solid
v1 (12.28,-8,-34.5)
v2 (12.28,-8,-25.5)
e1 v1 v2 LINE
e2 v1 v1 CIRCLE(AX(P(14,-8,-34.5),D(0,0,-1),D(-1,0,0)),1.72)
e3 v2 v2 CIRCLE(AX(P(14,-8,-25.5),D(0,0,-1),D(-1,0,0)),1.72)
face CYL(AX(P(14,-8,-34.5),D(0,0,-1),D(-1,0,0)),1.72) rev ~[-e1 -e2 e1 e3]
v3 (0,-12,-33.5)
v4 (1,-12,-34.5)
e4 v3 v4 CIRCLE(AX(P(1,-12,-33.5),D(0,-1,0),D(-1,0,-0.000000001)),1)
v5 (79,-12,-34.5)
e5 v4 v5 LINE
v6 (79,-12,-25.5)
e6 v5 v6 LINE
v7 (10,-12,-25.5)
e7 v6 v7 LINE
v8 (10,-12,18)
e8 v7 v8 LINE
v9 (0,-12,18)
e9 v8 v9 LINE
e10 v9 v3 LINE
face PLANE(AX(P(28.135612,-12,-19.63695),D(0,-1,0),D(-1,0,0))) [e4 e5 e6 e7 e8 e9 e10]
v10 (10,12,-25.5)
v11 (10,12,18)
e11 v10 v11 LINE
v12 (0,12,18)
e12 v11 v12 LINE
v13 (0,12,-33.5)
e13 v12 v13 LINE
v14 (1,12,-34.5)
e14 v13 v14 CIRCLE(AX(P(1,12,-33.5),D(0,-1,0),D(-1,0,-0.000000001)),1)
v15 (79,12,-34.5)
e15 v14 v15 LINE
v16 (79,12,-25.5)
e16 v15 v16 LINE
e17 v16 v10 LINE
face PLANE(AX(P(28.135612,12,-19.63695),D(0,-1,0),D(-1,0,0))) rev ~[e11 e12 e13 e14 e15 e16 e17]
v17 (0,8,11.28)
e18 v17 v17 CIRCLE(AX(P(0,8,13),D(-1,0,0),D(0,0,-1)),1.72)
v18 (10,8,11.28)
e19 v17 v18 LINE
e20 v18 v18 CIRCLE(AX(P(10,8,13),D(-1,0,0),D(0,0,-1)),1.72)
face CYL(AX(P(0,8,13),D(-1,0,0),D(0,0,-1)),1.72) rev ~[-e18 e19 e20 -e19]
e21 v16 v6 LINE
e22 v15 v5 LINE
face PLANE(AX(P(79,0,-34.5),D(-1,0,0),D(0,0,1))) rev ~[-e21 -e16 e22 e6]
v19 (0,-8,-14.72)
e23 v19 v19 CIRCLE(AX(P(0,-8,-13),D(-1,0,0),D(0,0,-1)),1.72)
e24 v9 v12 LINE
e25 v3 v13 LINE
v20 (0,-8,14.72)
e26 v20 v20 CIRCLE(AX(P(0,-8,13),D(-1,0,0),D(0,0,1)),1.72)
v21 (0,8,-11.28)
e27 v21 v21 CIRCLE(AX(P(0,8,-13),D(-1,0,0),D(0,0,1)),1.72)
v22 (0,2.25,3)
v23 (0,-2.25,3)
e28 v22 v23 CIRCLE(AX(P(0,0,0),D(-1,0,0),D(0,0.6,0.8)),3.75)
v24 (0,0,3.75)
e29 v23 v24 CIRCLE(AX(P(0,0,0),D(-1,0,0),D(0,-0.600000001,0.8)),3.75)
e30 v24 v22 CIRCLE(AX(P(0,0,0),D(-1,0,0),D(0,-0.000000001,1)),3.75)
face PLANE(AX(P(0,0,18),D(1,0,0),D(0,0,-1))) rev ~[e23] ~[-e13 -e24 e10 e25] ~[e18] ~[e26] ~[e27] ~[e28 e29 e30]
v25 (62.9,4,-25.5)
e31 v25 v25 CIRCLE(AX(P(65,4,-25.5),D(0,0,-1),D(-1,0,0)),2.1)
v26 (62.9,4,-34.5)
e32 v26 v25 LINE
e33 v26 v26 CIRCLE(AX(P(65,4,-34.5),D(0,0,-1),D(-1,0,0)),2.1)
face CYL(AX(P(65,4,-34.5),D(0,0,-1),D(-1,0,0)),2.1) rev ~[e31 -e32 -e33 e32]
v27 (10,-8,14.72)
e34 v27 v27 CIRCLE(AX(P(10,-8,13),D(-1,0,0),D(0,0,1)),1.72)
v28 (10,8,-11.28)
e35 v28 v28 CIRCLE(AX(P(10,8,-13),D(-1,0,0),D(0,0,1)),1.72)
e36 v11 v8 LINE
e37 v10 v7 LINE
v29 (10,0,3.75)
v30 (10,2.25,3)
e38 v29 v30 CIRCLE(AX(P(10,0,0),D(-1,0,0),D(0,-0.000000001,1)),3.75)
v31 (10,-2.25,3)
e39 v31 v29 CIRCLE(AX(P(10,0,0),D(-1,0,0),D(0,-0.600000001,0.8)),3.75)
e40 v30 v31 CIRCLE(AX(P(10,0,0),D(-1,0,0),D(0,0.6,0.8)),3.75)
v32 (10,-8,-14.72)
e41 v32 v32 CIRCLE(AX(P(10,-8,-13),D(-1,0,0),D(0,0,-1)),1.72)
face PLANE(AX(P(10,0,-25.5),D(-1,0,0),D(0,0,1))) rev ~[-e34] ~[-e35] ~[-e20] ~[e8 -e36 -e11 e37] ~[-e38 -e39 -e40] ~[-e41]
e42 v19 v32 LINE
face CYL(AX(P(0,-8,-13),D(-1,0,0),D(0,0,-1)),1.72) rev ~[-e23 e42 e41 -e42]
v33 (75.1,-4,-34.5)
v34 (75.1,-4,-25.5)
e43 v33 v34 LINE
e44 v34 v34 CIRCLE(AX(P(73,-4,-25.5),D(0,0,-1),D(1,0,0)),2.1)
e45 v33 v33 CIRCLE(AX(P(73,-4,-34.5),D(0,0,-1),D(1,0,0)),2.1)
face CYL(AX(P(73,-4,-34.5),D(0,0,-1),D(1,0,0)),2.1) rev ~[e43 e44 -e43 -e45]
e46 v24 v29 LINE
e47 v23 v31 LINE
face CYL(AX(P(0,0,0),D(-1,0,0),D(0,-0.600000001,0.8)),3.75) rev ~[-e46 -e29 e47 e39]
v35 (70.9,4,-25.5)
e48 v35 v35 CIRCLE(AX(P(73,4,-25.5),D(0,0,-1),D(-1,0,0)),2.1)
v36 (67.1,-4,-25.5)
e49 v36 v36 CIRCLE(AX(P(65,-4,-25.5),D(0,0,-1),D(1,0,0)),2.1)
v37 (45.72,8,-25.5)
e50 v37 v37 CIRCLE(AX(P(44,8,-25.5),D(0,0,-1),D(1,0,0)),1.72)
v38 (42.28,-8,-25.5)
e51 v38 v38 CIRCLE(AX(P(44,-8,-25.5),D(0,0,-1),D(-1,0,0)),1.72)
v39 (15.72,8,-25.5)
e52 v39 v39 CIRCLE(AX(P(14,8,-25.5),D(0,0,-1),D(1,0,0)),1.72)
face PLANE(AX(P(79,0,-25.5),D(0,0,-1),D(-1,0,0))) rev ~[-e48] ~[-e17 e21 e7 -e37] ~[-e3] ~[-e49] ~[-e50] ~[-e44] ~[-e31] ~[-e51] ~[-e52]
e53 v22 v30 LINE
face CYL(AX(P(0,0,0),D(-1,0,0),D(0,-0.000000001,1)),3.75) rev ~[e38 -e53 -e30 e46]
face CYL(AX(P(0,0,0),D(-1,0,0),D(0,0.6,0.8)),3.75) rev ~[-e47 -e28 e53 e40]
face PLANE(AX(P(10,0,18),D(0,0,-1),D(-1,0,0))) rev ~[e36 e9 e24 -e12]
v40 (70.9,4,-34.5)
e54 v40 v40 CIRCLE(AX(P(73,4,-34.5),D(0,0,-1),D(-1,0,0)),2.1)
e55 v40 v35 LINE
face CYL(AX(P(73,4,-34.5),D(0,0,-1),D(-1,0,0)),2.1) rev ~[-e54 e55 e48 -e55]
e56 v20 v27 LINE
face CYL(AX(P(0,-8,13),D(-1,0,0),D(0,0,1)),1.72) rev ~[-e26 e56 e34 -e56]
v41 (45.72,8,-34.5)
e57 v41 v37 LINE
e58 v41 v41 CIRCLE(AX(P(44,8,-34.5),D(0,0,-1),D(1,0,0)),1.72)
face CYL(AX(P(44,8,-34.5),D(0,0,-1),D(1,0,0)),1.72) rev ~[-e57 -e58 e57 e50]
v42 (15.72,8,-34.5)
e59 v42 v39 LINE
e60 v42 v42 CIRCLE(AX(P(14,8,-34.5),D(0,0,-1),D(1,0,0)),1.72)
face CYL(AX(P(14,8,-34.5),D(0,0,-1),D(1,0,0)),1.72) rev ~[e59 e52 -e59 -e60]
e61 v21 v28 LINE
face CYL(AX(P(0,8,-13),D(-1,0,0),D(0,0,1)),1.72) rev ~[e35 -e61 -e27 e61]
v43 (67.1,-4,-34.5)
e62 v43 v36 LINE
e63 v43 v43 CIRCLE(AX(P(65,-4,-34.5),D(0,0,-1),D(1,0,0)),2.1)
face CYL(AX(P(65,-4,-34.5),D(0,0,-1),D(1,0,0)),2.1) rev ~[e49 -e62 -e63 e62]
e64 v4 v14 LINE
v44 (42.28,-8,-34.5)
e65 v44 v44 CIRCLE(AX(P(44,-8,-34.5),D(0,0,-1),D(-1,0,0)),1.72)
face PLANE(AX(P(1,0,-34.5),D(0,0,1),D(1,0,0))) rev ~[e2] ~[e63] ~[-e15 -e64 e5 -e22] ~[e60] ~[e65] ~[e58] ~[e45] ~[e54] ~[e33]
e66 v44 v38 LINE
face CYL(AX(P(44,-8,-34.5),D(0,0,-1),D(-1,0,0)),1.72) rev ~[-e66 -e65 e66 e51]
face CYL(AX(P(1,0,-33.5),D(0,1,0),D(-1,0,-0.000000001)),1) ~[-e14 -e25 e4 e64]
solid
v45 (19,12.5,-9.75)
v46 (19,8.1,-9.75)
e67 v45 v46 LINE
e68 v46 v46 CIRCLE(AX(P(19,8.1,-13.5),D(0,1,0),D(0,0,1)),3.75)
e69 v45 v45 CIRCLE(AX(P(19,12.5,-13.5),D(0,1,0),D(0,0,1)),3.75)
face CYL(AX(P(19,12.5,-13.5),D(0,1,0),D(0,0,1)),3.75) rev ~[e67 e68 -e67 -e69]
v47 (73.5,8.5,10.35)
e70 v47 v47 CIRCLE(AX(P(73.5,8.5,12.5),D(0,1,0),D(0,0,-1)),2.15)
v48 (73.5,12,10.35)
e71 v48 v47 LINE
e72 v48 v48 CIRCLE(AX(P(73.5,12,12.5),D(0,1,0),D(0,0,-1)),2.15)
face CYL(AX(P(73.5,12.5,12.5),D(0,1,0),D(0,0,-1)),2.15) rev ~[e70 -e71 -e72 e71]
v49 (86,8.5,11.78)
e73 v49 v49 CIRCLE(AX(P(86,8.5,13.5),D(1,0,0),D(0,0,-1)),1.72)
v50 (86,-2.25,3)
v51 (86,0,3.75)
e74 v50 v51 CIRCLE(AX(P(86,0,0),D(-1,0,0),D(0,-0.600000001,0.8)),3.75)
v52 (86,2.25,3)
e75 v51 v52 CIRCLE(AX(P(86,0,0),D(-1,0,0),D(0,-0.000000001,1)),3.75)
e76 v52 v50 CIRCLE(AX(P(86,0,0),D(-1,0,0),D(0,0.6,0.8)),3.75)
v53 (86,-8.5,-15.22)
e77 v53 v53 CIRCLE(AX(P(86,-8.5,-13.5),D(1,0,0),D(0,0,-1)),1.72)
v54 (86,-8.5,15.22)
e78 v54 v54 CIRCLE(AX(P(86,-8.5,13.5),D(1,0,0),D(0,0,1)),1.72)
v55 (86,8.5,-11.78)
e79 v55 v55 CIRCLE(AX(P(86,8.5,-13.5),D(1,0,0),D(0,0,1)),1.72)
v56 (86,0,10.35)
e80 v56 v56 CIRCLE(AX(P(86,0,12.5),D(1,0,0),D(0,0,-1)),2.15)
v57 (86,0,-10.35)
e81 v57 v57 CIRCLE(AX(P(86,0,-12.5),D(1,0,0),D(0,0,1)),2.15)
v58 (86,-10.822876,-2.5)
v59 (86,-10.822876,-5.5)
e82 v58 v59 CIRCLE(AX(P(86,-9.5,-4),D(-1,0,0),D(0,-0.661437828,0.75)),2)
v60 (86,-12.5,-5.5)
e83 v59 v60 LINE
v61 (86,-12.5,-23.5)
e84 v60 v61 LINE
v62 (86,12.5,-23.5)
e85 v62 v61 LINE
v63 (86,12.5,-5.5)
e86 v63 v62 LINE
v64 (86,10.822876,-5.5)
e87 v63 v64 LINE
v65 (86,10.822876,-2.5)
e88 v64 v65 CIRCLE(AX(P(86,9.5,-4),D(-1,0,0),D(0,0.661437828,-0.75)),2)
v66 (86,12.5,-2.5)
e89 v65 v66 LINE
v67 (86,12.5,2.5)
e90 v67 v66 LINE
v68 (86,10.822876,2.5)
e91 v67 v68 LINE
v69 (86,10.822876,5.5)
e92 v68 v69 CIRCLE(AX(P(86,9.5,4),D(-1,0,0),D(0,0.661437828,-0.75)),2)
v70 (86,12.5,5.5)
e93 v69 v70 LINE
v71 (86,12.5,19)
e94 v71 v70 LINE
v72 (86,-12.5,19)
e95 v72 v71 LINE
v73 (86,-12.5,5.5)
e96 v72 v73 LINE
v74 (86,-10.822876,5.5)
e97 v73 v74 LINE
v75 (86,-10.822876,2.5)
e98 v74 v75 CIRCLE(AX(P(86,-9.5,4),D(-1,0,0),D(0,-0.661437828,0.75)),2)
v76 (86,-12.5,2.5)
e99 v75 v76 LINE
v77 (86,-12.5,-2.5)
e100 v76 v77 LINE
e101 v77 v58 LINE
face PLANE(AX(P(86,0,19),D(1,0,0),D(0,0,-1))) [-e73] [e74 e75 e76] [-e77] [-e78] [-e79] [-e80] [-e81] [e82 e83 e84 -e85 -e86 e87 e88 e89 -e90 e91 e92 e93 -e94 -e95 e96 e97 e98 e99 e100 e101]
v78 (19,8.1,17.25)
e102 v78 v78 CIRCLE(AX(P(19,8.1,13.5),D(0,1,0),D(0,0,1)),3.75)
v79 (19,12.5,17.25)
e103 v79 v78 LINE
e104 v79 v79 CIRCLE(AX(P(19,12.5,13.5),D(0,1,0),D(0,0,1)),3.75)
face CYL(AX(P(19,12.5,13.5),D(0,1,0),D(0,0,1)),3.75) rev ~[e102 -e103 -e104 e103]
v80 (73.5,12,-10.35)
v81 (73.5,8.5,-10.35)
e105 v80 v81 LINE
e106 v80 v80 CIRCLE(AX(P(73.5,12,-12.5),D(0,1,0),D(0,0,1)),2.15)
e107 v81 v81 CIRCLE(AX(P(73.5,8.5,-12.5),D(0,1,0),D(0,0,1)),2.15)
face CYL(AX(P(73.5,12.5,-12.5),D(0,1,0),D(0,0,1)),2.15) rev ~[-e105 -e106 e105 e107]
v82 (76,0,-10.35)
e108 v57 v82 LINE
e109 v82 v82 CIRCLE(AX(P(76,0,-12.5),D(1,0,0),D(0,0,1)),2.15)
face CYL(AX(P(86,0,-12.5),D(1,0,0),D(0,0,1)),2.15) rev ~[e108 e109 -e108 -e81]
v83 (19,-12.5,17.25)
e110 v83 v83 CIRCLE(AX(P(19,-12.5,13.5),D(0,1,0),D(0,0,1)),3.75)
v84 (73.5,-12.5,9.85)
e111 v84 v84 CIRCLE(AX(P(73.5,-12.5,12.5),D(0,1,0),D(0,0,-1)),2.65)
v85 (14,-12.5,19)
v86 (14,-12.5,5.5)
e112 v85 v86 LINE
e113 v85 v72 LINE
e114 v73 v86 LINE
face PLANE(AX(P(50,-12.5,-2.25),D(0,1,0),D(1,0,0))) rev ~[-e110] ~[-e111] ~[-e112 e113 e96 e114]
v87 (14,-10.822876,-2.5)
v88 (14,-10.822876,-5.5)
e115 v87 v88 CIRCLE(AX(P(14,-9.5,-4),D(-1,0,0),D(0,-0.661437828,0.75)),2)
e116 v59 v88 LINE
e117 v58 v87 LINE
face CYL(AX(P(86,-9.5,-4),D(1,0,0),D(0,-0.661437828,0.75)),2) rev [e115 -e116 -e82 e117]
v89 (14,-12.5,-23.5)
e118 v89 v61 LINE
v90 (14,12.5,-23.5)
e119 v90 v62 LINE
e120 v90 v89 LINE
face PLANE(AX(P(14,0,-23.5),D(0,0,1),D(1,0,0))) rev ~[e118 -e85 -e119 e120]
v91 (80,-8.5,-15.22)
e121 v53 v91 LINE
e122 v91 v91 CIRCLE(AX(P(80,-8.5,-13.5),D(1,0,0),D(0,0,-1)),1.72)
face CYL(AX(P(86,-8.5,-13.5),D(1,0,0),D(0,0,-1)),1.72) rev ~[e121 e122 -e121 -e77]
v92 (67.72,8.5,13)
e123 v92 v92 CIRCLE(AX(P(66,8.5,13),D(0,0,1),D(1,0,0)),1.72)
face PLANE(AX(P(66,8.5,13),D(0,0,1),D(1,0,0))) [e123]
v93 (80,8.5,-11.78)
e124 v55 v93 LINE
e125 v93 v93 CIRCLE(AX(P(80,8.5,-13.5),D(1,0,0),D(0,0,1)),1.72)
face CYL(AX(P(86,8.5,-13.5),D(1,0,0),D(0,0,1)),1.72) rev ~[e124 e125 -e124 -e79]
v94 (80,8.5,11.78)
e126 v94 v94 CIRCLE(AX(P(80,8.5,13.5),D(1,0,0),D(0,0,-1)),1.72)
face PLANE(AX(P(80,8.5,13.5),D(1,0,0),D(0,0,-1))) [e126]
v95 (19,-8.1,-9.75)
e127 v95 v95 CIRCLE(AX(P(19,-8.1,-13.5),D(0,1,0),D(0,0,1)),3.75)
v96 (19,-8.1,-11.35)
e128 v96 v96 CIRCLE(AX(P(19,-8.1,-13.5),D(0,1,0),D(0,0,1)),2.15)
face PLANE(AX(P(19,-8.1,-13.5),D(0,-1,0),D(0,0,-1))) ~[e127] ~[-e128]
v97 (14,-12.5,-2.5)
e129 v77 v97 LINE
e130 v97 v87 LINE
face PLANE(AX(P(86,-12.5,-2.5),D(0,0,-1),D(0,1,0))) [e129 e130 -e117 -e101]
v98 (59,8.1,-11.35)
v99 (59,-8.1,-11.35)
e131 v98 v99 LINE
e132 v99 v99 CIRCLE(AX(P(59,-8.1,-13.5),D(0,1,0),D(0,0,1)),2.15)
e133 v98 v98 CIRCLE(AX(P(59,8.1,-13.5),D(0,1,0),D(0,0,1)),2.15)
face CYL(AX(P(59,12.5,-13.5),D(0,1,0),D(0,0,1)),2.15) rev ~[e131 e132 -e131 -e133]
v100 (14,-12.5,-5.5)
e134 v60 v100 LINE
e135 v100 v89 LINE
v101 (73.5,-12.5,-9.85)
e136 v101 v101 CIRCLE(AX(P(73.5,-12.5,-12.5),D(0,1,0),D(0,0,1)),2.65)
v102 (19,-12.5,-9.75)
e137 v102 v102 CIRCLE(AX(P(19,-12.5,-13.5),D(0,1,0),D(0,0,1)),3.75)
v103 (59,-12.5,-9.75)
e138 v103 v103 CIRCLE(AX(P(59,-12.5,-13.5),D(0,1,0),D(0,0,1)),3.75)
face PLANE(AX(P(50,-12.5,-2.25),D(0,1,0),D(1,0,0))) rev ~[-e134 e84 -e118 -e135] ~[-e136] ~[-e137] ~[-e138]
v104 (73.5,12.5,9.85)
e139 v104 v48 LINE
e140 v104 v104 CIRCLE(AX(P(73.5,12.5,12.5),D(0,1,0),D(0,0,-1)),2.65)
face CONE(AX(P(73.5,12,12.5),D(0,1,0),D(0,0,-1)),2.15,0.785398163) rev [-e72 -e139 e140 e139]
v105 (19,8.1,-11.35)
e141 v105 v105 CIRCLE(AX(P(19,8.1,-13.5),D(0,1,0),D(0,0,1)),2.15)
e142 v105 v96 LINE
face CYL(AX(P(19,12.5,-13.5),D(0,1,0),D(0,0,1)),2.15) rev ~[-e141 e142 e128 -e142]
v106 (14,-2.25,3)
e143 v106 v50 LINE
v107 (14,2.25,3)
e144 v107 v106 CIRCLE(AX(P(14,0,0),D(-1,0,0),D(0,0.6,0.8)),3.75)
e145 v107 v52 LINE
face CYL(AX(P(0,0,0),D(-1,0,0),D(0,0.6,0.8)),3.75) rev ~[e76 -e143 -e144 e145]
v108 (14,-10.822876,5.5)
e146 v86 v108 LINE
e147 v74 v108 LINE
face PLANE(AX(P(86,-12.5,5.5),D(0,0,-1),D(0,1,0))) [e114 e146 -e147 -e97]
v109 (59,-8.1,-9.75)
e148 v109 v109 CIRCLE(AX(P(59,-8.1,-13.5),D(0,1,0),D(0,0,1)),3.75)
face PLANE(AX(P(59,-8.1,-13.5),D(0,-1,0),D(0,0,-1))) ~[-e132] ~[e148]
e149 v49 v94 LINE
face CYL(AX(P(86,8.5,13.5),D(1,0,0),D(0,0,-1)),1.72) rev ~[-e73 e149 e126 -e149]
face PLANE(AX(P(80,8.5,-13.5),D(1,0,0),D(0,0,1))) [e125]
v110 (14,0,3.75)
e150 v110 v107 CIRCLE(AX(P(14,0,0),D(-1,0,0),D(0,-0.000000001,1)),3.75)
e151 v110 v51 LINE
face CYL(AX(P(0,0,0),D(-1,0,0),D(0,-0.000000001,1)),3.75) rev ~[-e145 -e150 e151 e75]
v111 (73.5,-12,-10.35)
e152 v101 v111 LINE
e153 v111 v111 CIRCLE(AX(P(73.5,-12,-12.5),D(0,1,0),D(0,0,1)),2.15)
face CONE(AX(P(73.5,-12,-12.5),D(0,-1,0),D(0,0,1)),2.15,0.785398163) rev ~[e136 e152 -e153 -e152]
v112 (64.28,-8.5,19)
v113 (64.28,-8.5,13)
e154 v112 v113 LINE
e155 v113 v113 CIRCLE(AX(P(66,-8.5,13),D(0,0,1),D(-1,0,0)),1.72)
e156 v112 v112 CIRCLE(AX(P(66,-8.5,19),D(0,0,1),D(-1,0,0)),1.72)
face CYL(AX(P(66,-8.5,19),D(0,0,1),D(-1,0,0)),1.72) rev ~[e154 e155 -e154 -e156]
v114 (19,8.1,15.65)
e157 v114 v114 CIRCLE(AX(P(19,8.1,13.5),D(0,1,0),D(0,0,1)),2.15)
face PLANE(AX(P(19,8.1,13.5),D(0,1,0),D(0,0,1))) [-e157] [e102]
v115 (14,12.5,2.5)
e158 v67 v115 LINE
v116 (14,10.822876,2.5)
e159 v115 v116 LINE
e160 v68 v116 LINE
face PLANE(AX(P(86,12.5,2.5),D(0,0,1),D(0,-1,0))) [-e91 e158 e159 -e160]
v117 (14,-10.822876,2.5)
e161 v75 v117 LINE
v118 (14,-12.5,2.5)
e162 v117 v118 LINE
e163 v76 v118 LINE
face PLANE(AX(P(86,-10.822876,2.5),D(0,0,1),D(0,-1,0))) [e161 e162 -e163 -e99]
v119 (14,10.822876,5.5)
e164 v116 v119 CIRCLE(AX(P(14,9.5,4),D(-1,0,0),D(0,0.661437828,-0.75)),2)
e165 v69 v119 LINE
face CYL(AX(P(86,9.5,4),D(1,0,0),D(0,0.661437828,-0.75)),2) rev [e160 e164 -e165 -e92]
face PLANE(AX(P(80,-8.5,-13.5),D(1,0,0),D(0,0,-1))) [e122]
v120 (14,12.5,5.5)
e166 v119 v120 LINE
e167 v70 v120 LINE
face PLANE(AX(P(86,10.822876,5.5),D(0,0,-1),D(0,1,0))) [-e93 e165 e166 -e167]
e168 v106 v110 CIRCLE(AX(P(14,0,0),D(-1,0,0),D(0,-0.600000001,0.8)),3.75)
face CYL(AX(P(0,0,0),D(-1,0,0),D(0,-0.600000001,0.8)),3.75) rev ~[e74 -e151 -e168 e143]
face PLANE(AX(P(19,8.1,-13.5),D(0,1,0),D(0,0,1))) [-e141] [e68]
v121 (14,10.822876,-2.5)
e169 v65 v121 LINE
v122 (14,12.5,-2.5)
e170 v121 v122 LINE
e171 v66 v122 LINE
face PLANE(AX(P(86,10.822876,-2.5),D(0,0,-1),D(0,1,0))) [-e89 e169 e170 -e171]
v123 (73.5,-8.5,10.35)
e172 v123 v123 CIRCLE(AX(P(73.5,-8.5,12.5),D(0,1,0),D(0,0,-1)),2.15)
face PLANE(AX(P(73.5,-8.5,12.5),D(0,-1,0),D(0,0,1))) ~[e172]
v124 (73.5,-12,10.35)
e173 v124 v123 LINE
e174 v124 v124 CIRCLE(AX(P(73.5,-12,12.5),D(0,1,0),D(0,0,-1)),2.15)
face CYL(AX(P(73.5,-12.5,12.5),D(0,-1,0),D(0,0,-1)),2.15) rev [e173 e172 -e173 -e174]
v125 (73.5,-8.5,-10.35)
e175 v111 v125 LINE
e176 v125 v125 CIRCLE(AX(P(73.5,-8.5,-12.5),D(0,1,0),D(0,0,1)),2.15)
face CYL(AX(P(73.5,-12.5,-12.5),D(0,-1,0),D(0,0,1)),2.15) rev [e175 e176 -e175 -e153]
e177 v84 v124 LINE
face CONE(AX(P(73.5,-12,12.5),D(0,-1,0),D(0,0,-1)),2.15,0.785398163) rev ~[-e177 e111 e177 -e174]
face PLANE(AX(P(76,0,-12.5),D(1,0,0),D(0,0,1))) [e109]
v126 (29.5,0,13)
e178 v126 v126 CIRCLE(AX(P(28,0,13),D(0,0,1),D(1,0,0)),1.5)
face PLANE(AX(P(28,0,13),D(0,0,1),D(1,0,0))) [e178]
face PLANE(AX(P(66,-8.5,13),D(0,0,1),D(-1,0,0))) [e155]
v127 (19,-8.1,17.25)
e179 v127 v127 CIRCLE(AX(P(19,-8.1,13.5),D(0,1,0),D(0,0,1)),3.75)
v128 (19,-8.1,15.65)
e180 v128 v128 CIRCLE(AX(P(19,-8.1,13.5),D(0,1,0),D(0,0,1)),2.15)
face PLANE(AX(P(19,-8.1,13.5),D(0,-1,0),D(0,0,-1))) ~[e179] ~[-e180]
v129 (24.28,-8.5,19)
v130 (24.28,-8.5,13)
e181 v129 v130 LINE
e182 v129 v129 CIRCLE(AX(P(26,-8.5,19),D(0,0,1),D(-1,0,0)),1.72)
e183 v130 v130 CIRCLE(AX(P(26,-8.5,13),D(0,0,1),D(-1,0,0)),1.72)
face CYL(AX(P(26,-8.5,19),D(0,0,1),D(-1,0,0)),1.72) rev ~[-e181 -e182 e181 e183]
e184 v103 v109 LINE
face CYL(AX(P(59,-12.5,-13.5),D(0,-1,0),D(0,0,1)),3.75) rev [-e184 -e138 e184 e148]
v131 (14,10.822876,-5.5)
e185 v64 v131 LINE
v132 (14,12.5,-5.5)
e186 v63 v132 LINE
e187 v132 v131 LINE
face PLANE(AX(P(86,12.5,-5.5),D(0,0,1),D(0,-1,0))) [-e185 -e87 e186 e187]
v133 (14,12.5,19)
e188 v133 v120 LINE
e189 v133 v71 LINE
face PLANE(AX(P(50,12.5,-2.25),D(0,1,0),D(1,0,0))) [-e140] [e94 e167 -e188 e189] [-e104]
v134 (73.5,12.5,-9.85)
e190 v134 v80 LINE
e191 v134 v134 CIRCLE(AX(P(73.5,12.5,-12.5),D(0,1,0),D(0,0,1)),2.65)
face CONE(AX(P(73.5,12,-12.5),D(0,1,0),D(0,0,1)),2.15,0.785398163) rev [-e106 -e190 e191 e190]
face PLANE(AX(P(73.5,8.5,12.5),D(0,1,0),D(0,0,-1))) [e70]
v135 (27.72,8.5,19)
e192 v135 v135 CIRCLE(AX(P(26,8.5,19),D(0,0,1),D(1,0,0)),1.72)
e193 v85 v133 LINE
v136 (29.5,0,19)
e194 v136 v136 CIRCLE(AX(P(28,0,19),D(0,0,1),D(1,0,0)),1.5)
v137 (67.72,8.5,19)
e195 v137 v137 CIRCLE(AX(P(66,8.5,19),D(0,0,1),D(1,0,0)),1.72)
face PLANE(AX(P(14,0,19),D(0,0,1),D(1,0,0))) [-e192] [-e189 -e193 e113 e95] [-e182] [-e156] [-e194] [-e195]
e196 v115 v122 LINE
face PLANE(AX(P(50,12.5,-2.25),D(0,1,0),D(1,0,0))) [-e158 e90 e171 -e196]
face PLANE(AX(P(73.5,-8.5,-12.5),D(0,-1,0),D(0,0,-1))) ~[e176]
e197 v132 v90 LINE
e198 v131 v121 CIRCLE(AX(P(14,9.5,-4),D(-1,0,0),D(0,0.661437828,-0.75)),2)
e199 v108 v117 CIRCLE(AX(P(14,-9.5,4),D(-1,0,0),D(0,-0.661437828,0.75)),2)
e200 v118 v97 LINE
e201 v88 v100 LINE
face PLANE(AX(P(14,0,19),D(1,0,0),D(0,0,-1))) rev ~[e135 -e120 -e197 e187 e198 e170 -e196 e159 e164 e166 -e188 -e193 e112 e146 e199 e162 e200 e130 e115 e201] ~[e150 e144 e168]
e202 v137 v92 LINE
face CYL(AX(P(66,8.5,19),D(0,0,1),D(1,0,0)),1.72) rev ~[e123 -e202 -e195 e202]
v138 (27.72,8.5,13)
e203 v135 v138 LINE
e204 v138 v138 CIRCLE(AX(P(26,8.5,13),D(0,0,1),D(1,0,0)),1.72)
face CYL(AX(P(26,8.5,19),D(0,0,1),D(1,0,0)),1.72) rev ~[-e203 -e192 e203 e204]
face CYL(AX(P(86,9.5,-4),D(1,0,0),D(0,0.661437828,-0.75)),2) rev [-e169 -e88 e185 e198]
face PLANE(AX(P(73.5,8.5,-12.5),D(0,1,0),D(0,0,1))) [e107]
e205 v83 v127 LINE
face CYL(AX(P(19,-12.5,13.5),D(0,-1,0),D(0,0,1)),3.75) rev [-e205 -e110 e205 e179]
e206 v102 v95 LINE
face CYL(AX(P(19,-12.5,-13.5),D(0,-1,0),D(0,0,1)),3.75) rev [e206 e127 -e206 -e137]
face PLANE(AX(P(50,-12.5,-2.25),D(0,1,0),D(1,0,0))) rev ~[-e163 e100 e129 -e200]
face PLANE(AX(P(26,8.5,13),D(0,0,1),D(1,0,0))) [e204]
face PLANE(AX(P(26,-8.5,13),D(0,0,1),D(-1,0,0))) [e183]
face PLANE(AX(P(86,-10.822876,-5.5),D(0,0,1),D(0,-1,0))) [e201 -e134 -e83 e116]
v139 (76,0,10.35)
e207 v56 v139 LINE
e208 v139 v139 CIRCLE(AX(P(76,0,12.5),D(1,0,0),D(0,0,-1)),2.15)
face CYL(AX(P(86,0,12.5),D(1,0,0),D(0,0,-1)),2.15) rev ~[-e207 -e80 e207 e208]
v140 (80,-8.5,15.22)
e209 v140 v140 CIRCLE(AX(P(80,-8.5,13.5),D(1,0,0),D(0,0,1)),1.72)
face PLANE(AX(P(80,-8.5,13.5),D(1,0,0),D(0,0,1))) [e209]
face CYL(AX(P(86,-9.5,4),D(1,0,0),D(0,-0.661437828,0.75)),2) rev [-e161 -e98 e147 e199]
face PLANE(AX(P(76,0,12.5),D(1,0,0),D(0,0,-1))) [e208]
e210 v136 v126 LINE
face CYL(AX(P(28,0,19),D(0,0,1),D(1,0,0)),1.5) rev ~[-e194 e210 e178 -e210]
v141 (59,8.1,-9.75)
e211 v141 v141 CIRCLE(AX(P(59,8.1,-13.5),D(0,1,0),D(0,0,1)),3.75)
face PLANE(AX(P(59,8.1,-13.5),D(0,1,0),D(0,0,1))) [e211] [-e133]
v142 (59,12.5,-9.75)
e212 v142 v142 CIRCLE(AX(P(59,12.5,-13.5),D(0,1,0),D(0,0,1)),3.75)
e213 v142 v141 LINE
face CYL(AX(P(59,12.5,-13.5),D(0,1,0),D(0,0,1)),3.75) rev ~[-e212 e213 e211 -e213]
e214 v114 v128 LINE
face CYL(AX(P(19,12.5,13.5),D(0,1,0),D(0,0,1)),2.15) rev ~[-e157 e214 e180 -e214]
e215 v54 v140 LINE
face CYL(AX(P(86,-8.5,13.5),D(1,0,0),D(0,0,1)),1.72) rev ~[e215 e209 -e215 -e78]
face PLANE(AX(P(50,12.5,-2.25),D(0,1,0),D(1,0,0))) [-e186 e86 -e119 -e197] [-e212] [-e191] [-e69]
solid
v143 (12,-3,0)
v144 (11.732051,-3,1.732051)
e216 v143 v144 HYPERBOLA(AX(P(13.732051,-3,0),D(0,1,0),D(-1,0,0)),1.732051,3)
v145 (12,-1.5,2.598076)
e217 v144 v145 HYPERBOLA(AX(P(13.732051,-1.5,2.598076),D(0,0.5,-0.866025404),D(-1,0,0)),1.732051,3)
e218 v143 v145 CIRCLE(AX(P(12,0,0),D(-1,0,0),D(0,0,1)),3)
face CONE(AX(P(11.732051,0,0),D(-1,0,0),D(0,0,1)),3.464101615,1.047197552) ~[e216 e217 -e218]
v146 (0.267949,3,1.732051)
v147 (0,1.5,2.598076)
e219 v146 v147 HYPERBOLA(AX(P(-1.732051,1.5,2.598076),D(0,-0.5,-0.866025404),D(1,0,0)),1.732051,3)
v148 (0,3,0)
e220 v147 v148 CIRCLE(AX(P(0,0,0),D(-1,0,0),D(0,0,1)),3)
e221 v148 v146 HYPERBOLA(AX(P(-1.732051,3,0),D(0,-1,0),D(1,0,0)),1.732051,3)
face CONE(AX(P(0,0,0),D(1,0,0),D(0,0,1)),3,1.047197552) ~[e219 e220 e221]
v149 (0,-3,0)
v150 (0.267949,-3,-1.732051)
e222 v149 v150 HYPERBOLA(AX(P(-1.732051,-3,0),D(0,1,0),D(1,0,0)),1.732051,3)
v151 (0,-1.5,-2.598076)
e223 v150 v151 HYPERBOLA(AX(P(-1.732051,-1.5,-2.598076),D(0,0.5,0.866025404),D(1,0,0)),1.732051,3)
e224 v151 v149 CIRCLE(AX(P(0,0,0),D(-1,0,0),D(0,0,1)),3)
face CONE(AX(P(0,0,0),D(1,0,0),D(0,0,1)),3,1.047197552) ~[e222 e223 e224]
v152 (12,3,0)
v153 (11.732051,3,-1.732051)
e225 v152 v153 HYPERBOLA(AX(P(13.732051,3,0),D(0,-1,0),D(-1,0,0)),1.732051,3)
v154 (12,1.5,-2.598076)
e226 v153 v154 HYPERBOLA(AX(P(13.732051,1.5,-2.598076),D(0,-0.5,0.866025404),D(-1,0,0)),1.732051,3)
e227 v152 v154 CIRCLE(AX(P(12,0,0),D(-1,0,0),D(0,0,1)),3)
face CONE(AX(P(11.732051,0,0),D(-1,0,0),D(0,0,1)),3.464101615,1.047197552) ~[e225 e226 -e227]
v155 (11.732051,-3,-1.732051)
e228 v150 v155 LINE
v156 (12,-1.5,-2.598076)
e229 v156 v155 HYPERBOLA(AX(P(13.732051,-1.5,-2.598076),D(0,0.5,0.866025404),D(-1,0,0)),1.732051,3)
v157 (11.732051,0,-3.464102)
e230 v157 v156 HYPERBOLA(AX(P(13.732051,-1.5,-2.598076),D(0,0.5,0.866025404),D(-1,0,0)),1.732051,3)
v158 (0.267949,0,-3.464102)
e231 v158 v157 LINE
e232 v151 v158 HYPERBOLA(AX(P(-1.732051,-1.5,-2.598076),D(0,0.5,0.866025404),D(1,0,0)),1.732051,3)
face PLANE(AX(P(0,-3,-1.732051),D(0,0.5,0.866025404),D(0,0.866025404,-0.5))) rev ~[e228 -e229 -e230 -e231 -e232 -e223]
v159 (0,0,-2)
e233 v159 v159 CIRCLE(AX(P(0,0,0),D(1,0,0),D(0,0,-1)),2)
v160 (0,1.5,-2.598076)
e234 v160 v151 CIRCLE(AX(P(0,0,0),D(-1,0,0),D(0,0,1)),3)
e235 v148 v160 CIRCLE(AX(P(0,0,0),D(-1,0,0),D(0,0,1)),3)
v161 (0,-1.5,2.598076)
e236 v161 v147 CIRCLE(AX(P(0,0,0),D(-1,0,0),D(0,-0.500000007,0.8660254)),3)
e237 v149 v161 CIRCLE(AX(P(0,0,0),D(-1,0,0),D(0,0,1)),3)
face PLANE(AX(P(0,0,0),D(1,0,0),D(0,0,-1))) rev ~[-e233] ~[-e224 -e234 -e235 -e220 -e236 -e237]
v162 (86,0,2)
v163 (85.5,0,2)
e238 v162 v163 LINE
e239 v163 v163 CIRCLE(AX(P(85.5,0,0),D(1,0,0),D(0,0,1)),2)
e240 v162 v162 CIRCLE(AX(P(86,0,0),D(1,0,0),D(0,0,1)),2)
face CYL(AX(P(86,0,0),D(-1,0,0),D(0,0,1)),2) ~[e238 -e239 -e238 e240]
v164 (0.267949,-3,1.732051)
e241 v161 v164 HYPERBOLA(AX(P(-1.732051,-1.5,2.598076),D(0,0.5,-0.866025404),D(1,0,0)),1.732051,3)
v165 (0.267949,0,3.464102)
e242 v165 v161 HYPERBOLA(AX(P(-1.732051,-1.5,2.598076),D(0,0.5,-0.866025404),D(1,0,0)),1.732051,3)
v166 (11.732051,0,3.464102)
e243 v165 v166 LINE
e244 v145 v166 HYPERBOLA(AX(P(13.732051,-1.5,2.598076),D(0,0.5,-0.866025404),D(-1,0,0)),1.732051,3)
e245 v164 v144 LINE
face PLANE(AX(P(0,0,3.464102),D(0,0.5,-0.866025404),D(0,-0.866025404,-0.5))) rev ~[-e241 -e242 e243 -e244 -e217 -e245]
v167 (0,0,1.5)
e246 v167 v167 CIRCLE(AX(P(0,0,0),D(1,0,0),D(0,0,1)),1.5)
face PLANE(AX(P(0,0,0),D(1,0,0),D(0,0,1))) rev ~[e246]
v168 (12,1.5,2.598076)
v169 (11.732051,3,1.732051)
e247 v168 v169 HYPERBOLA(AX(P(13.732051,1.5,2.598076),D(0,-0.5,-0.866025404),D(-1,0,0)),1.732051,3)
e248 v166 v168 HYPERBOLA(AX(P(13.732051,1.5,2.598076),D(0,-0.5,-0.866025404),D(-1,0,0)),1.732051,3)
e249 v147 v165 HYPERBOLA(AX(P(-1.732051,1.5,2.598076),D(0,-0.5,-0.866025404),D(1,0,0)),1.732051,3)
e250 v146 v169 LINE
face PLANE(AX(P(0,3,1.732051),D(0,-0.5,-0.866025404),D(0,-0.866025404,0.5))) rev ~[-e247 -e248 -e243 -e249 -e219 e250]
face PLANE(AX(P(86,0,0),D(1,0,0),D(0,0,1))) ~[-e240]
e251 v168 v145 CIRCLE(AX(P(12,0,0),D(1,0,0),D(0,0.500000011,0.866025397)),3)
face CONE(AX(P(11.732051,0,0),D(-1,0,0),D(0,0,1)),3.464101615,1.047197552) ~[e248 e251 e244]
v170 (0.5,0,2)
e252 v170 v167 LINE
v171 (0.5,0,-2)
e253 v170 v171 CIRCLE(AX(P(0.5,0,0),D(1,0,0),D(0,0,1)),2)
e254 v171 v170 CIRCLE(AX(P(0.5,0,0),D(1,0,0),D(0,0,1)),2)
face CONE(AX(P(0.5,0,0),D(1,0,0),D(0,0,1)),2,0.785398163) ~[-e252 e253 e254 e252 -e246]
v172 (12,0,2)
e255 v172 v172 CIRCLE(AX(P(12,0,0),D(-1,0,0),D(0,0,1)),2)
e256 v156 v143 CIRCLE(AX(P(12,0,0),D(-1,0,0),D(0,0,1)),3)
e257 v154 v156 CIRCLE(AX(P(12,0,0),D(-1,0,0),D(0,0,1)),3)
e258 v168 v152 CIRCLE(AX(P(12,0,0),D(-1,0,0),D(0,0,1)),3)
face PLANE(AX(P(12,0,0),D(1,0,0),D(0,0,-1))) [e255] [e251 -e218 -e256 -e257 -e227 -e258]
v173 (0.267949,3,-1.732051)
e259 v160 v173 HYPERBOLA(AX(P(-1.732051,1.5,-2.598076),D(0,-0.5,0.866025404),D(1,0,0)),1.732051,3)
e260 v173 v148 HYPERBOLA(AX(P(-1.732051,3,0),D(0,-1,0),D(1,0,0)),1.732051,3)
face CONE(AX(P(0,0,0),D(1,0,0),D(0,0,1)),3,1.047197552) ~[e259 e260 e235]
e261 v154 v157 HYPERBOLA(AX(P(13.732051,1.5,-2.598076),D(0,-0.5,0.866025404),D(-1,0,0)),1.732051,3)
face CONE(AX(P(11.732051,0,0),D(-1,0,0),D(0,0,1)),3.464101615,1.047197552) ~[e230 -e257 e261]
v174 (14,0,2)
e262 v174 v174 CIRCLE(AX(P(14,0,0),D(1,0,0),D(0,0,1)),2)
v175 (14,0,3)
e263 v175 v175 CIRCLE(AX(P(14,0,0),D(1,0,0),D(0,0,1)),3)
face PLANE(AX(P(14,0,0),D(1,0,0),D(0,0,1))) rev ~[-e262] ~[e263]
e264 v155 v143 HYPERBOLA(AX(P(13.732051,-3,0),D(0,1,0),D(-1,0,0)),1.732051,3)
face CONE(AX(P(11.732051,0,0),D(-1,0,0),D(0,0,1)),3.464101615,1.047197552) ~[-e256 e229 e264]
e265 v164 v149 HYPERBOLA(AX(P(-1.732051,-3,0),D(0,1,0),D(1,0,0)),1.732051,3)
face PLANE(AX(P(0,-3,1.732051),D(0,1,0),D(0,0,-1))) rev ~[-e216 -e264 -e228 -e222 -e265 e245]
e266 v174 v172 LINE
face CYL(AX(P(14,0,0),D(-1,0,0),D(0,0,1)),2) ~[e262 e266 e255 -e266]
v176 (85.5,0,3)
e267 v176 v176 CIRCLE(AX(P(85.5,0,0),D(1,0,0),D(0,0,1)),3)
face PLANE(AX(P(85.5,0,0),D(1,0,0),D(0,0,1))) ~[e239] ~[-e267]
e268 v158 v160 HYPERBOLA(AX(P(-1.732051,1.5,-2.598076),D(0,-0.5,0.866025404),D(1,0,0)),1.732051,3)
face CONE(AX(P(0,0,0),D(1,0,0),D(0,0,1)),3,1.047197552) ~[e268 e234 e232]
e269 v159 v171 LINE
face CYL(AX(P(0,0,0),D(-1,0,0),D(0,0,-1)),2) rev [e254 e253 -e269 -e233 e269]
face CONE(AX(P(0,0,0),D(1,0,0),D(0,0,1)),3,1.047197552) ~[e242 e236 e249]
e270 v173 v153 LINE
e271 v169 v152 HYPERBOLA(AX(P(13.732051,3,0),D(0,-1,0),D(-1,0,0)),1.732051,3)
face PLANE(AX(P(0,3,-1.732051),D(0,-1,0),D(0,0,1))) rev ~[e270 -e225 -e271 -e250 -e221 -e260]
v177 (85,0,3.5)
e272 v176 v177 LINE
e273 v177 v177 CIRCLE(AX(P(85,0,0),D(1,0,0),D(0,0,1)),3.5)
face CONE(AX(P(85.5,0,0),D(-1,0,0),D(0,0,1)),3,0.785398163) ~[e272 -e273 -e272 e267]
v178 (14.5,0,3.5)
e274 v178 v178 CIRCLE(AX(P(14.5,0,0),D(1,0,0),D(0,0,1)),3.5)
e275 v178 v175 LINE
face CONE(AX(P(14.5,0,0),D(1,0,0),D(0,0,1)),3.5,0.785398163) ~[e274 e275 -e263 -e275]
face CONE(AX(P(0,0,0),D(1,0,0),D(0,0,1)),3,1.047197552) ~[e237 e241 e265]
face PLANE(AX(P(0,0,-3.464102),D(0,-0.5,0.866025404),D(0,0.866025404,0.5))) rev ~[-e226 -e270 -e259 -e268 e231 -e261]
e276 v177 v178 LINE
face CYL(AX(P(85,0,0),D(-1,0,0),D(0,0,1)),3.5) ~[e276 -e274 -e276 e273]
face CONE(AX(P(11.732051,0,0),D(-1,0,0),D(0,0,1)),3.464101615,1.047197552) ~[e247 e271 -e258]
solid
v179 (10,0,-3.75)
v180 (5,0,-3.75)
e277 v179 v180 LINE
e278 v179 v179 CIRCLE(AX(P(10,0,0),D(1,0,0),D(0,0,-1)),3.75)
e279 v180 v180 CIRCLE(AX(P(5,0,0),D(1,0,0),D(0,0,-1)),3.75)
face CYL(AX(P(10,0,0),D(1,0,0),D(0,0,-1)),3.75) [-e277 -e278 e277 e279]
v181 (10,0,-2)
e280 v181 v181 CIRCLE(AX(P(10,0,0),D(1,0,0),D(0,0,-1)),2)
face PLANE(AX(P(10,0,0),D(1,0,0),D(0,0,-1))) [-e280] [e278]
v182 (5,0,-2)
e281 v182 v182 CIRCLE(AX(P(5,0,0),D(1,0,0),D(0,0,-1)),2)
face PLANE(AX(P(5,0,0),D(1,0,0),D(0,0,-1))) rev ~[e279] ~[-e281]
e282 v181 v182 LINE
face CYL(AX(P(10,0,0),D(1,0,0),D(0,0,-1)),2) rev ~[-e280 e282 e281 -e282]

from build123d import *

# Parameters (mm, degrees)
EXTRUDE_1_DEPTH      = 12
SKETCH_3_W           = 72
SKETCH_3_H           = 42.5
EXTRUDE_2_DEPTH      = 12.5
CUT_EXTRUDE_1_DEPTH  = 72
SKETCH_6_R           = 1.72
CUT_EXTRUDE_2_DEPTH  = 6
SKETCH_7_R           = 2.15
CUT_EXTRUDE_3_DEPTH  = 10
SKETCH_8_R           = 2.15
CUT_EXTRUDE_4_DEPTH  = 25
SKETCH_9_R           = 2.15
CUT_EXTRUDE_5_DEPTH  = 4
SKETCH_10_R          = 3.75
CUT_EXTRUDE_6_DEPTH  = 4.4
CHAMFER_2_SIZE       = 0.5
SKETCH_11_R          = 1.72
SKETCH_11_R_2        = 1.5
CUT_EXTRUDE_7_DEPTH  = 6
SKETCH_12_R          = 1.72
SKETCH_12_R_2        = 2.1
CUT_EXTRUDE_8_DEPTH  = 9
SKETCH_14_R          = 1.72
CUT_EXTRUDE_9_DEPTH  = 10
EXTRUDE_3_REACH      = 86.395
SKETCH_16_R          = 2.5
CUT_EXTRUDE_12_DEPTH = 94.501336889
SKETCH_21_R          = 3.75
SKETCH_21_R_2        = 2
EXTRUDE_5_DEPTH      = 5
EXTRUDE_4_DEPTH      = 2
EXTRUDE_4_DEPTH_BACK = 10
SKETCH_17_R          = 2


with BuildPart() as part:
    # 草图2 → 凸台-拉伸1 (new, symmetric)
    with BuildSketch(Plane(origin=(0, 0, 0), x_dir=(1, 0, 0), z_dir=(0, 1, 0))):
        with BuildLine():
            Line((1, 34.5), (79, 34.5))
            Line((79, 34.5), (79, 25.5))
            Line((79, 25.5), (10, 25.5))
            Line((10, 25.5), (10, -18))
            Line((10, -18), (0, -18))
            Line((0, -18), (0, 33.5))
            ThreePointArc((0, 33.5), (0.292893219, 34.207106781), (1, 34.5))
        make_face()
    extrude(amount=EXTRUDE_1_DEPTH, both=True)

    # 草图12 → 切除-拉伸8 (cut)
    with BuildSketch(Plane(origin=(0, 0, -34.5), x_dir=(-1, 0, 0), z_dir=(0, 0, -1))):
        with Locations((-14, -8)):
            Circle(SKETCH_12_R)
        with Locations((-44, -8)):
            Circle(SKETCH_12_R)
        with Locations(Location((-44, 8, 0), (0, 0, 180))):
            Circle(SKETCH_12_R)
        with Locations(Location((-14, 8, 0), (0, 0, 180))):
            Circle(SKETCH_12_R)
        with Locations((-73, 4)):
            Circle(SKETCH_12_R_2)
        with Locations((-65, 4)):
            Circle(SKETCH_12_R_2)
        with Locations(Location((-65, -4, 0), (0, 0, 180))):
            Circle(SKETCH_12_R_2)
        with Locations(Location((-73, -4, 0), (0, 0, 180))):
            Circle(SKETCH_12_R_2)
    extrude(amount=-CUT_EXTRUDE_8_DEPTH, mode=Mode.SUBTRACT)

    # 草图14 → 切除-拉伸9 (cut)
    with BuildSketch(Plane.ZY):
        with Locations((13, -8)):
            Circle(SKETCH_14_R)
        with Locations(Location((13, 8, 0), (0, 0, 180))):
            Circle(SKETCH_14_R)
        with Locations(Location((-13, -8, 0), (0, 0, 180))):
            Circle(SKETCH_14_R)
        with Locations((-13, 8)):
            Circle(SKETCH_14_R)
    extrude(amount=-CUT_EXTRUDE_9_DEPTH, mode=Mode.SUBTRACT)


with BuildPart() as body_2:
    # 草图3 → 凸台-拉伸2 (new, symmetric)
    with BuildSketch(Plane(origin=(0, 0, 0), x_dir=(1, 0, 0), z_dir=(0, 1, 0))):
        with Locations((50, 2.25)):
            Rectangle(SKETCH_3_W, SKETCH_3_H)
    extrude(amount=EXTRUDE_2_DEPTH, both=True)

    # 草图5 → 切除-拉伸1 (cut)
    with BuildSketch(Plane(origin=(86, 0, 0), x_dir=(0, 0, -1), z_dir=(1, 0, 0))):
        with BuildLine():
            Line((-5.5, 10.822875656), (-5.5, 12.5))
            Line((-5.5, 12.5), (-2.5, 12.5))
            Line((-2.5, 12.5), (-2.5, 10.822875656))
            ThreePointArc((-2.5, 10.822875656), (-4, 7.5), (-5.5, 10.822875656))
        make_face()
        with BuildLine():
            Line((-2.5, -10.822875656), (-2.5, -12.5))
            Line((-2.5, -12.5), (-5.5, -12.5))
            Line((-5.5, -12.5), (-5.5, -10.822875656))
            ThreePointArc((-5.5, -10.822875656), (-4, -7.5), (-2.5, -10.822875656))
        make_face()
        with BuildLine():
            Line((5.5, -10.822875656), (5.5, -12.5))
            Line((5.5, -12.5), (2.5, -12.5))
            Line((2.5, -12.5), (2.5, -10.822875656))
            ThreePointArc((2.5, -10.822875656), (4, -7.5), (5.5, -10.822875656))
        make_face()
        with BuildLine():
            Line((2.5, 10.822875656), (2.5, 12.5))
            Line((2.5, 12.5), (5.5, 12.5))
            Line((5.5, 12.5), (5.5, 10.822875656))
            ThreePointArc((5.5, 10.822875656), (4, 7.5), (2.5, 10.822875656))
        make_face()
    extrude(amount=-CUT_EXTRUDE_1_DEPTH, mode=Mode.SUBTRACT)

    # 草图6 → 切除-拉伸2 (cut)
    with BuildSketch(Plane(origin=(86, 0, 0), x_dir=(0, 0, -1), z_dir=(1, 0, 0))):
        with Locations((-13.5, 8.5)):
            Circle(SKETCH_6_R)
        with Locations(Location((-13.5, -8.5, 0), (0, 0, 180))):
            Circle(SKETCH_6_R)
        with Locations((13.5, -8.5)):
            Circle(SKETCH_6_R)
        with Locations(Location((13.5, 8.5, 0), (0, 0, 180))):
            Circle(SKETCH_6_R)
    extrude(amount=-CUT_EXTRUDE_2_DEPTH, mode=Mode.SUBTRACT)

    # 草图7 → 切除-拉伸3 (cut)
    with BuildSketch(Plane(origin=(86, 0, 0), x_dir=(0, 0, -1), z_dir=(1, 0, 0))):
        with Locations((-12.5, 0)):
            Circle(SKETCH_7_R)
        with Locations(Location((12.5, 0, 0), (0, 0, 180))):
            Circle(SKETCH_7_R)
    extrude(amount=-CUT_EXTRUDE_3_DEPTH, mode=Mode.SUBTRACT)

    # 草图8 → 切除-拉伸4 (cut)
    with BuildSketch(Plane(origin=(0, 12.5, 0), x_dir=(1, 0, 0), z_dir=(0, 1, 0))):
        with Locations(Location((19, 13.5, 0), (0, 0, 270))):
            Circle(SKETCH_8_R)
        with Locations(Location((59, 13.5, 0), (0, 0, 270))):
            Circle(SKETCH_8_R)
        with Locations(Location((19, -13.5, 0), (0, 0, 270))):
            Circle(SKETCH_8_R)
    extrude(amount=-CUT_EXTRUDE_4_DEPTH, mode=Mode.SUBTRACT)

    # 草图9 → 切除-拉伸5 (cut)
    with BuildSketch(Plane(origin=(0, 12.5, 0), x_dir=(1, 0, 0), z_dir=(0, 1, 0))):
        with Locations(Location((73.5, 12.5, 0), (0, 0, 270))):
            Circle(SKETCH_9_R)
        with Locations(Location((73.5, -12.5, 0), (0, 0, 90))):
            Circle(SKETCH_9_R)
    cut_extrude_5 = extrude(amount=-CUT_EXTRUDE_5_DEPTH, mode=Mode.SUBTRACT)

    # 草图10 → 切除-拉伸6 (cut)
    with BuildSketch(Plane(origin=(0, 12.5, 0), x_dir=(1, 0, 0), z_dir=(0, 1, 0))):
        with Locations(Location((19, 13.5, 0), (0, 0, 270))):
            Circle(SKETCH_10_R)
        with Locations(Location((59, 13.5, 0), (0, 0, 270))):
            Circle(SKETCH_10_R)
        with Locations(Location((19, -13.5, 0), (0, 0, 270))):
            Circle(SKETCH_10_R)
    cut_extrude_6 = extrude(amount=-CUT_EXTRUDE_6_DEPTH, mode=Mode.SUBTRACT)

    # 镜向1: 切除-拉伸5, 切除-拉伸6 across plane
    add(cut_extrude_5.mirror(Plane.ZX), mode=Mode.SUBTRACT)
    add(cut_extrude_6.mirror(Plane.ZX), mode=Mode.SUBTRACT)

    # 倒角2
    chamfer_2_edges = [body_2.edges().sort_by_distance(p)[0] for p in [
        (73.5, 12.5, -14.65),
        (73.5, 12.5, 14.65),
        (73.5, -12.5, -14.65),
        (73.5, -12.5, 14.65),
    ]]
    chamfer(chamfer_2_edges, length=CHAMFER_2_SIZE)

    # 草图11 → 切除-拉伸7 (cut)
    with BuildSketch(Plane.XY.offset(19)):
        with Locations((26, 8.5)):
            Circle(SKETCH_11_R)
        with Locations((66, 8.5)):
            Circle(SKETCH_11_R)
        with Locations(Location((66, -8.5, 0), (0, 0, 180))):
            Circle(SKETCH_11_R)
        with Locations(Location((26, -8.5, 0), (0, 0, 180))):
            Circle(SKETCH_11_R)
        with Locations((28, 0)):
            Circle(SKETCH_11_R_2)
    extrude(amount=-CUT_EXTRUDE_7_DEPTH, mode=Mode.SUBTRACT)

    # 草图16 → 凸台-拉伸3 (add, up to next)
    with BuildSketch(Plane(origin=(10, 0, 0), x_dir=(0, 0, -1), z_dir=(1, 0, 0)), mode=Mode.PRIVATE) as extrude_3_sk1:
        with Locations(Location((0, 0, 0), (0, 0, 180))):
            Circle(SKETCH_16_R)
    extrude_3_tool1 = extrude(extrude_3_sk1.sketch, amount=EXTRUDE_3_REACH, mode=Mode.PRIVATE) - body_2.part

    add(part.part)  # 凸台-拉伸3 merges part
    add(extrude_3_tool1.solids().sort_by_distance((10, 0, 0))[0])

    # 草图18 → 切除-拉伸12 (cut, through all)
    with BuildSketch(Plane.ZY):
        with BuildLine():
            Line((3, 2.25), (3, -2.25))
            ThreePointArc((3, -2.25), (3.557562368, -1.185854123), (3.75, 0))
            ThreePointArc((3.75, 0), (3.557562368, 1.185854123), (3, 2.25))
        make_face()
        with BuildLine():
            ThreePointArc((-3, 2.25), (-3.75, 0), (-3, -2.25))
            Line((-3, -2.25), (-3, 2.25))
        make_face()
        with BuildLine():
            ThreePointArc((-3, -2.25), (0, -3.75), (3, -2.25))
            Line((3, -2.25), (3, 2.25))
            ThreePointArc((3, 2.25), (0, 3.75), (-3, 2.25))
            Line((-3, 2.25), (-3, -2.25))
        make_face()
    extrude(amount=-CUT_EXTRUDE_12_DEPTH, mode=Mode.SUBTRACT)


with BuildPart() as cut_extrude_12_piece_1:
    # of the separate pieces the step leaves, piece 1, a body of its own (cut_extrude_12_pieces)
    add(body_2.part.solids().sort_by_distance((14, -12.5, 19))[0])


with BuildPart() as cut_extrude_12_piece_2:
    # of the separate pieces the step leaves, piece 2, a body of its own (cut_extrude_12_pieces)
    add(body_2.part.solids().sort_by_distance((0, -12, -33.5))[0])


with BuildPart() as body_3:
    # 草图21 → 凸台-拉伸5 (new body)
    with BuildSketch(Plane(origin=(10, 0, 0), x_dir=(0, 0, -1), z_dir=(1, 0, 0))):
        Circle(SKETCH_21_R)
        Circle(SKETCH_21_R_2, mode=Mode.SUBTRACT)
    extrude(amount=-EXTRUDE_5_DEPTH)


with BuildPart() as body_4:
    # 草图17 → 凸台-拉伸4 (new, two sides: drawn at the far end of the back side and taken through both)
    with BuildSketch(Plane(origin=(10, 0, 0), x_dir=(0, 0, -1), z_dir=(1, 0, 0)).offset(-EXTRUDE_4_DEPTH_BACK)):
        Polygon((3.464101615, 0), (1.732050808, 3), (-1.732050808, 3), (-3.464101615, 0), (-1.732050808, -3), (1.732050808, -3), align=None)
        Circle(SKETCH_17_R, mode=Mode.SUBTRACT)
    extrude(amount=EXTRUDE_4_DEPTH + EXTRUDE_4_DEPTH_BACK)

    # 草图19 → 切除-旋转1 (revolve, cut)
    with BuildSketch(Plane(origin=(0, 0, 0), x_dir=(1, 0, 0), z_dir=(0, 1, 0)), mode=Mode.PRIVATE) as cut_revolve_1_sk:
        Polygon((11.732050808, 3.464101615), (12, 3), (12, 3.464101615), align=None)
        Polygon((0, 3.464101615), (0, 3), (0.267949192, 3.464101615), align=None)
    revolve(cut_revolve_1_sk.sketch.rotate(Axis((20.777211293, 0, 0), (-1, 0, 0)), 180), axis=Axis((20.777211293, 0, 0), (-1, 0, 0)), mode=Mode.SUBTRACT)

    # 草图20 → 旋转1 (revolve)
    with BuildSketch(Plane.XY, mode=Mode.PRIVATE) as revolve_1_sk:
        Polygon((0, 1.5), (0, 0), (86, 0), (86, 2), (85.5, 2), (85.5, 3), (85, 3.5), (14.5, 3.5), (14, 3), (14, 2), (0.5, 2), align=None)
    revolve(revolve_1_sk.sketch.rotate(Axis((0, 0, 0), (1, 0, 0)), 90), axis=Axis((0, 0, 0), (1, 0, 0)))


solid = Compound([cut_extrude_12_piece_1.part, cut_extrude_12_piece_2.part, body_3.part, body_4.part])
